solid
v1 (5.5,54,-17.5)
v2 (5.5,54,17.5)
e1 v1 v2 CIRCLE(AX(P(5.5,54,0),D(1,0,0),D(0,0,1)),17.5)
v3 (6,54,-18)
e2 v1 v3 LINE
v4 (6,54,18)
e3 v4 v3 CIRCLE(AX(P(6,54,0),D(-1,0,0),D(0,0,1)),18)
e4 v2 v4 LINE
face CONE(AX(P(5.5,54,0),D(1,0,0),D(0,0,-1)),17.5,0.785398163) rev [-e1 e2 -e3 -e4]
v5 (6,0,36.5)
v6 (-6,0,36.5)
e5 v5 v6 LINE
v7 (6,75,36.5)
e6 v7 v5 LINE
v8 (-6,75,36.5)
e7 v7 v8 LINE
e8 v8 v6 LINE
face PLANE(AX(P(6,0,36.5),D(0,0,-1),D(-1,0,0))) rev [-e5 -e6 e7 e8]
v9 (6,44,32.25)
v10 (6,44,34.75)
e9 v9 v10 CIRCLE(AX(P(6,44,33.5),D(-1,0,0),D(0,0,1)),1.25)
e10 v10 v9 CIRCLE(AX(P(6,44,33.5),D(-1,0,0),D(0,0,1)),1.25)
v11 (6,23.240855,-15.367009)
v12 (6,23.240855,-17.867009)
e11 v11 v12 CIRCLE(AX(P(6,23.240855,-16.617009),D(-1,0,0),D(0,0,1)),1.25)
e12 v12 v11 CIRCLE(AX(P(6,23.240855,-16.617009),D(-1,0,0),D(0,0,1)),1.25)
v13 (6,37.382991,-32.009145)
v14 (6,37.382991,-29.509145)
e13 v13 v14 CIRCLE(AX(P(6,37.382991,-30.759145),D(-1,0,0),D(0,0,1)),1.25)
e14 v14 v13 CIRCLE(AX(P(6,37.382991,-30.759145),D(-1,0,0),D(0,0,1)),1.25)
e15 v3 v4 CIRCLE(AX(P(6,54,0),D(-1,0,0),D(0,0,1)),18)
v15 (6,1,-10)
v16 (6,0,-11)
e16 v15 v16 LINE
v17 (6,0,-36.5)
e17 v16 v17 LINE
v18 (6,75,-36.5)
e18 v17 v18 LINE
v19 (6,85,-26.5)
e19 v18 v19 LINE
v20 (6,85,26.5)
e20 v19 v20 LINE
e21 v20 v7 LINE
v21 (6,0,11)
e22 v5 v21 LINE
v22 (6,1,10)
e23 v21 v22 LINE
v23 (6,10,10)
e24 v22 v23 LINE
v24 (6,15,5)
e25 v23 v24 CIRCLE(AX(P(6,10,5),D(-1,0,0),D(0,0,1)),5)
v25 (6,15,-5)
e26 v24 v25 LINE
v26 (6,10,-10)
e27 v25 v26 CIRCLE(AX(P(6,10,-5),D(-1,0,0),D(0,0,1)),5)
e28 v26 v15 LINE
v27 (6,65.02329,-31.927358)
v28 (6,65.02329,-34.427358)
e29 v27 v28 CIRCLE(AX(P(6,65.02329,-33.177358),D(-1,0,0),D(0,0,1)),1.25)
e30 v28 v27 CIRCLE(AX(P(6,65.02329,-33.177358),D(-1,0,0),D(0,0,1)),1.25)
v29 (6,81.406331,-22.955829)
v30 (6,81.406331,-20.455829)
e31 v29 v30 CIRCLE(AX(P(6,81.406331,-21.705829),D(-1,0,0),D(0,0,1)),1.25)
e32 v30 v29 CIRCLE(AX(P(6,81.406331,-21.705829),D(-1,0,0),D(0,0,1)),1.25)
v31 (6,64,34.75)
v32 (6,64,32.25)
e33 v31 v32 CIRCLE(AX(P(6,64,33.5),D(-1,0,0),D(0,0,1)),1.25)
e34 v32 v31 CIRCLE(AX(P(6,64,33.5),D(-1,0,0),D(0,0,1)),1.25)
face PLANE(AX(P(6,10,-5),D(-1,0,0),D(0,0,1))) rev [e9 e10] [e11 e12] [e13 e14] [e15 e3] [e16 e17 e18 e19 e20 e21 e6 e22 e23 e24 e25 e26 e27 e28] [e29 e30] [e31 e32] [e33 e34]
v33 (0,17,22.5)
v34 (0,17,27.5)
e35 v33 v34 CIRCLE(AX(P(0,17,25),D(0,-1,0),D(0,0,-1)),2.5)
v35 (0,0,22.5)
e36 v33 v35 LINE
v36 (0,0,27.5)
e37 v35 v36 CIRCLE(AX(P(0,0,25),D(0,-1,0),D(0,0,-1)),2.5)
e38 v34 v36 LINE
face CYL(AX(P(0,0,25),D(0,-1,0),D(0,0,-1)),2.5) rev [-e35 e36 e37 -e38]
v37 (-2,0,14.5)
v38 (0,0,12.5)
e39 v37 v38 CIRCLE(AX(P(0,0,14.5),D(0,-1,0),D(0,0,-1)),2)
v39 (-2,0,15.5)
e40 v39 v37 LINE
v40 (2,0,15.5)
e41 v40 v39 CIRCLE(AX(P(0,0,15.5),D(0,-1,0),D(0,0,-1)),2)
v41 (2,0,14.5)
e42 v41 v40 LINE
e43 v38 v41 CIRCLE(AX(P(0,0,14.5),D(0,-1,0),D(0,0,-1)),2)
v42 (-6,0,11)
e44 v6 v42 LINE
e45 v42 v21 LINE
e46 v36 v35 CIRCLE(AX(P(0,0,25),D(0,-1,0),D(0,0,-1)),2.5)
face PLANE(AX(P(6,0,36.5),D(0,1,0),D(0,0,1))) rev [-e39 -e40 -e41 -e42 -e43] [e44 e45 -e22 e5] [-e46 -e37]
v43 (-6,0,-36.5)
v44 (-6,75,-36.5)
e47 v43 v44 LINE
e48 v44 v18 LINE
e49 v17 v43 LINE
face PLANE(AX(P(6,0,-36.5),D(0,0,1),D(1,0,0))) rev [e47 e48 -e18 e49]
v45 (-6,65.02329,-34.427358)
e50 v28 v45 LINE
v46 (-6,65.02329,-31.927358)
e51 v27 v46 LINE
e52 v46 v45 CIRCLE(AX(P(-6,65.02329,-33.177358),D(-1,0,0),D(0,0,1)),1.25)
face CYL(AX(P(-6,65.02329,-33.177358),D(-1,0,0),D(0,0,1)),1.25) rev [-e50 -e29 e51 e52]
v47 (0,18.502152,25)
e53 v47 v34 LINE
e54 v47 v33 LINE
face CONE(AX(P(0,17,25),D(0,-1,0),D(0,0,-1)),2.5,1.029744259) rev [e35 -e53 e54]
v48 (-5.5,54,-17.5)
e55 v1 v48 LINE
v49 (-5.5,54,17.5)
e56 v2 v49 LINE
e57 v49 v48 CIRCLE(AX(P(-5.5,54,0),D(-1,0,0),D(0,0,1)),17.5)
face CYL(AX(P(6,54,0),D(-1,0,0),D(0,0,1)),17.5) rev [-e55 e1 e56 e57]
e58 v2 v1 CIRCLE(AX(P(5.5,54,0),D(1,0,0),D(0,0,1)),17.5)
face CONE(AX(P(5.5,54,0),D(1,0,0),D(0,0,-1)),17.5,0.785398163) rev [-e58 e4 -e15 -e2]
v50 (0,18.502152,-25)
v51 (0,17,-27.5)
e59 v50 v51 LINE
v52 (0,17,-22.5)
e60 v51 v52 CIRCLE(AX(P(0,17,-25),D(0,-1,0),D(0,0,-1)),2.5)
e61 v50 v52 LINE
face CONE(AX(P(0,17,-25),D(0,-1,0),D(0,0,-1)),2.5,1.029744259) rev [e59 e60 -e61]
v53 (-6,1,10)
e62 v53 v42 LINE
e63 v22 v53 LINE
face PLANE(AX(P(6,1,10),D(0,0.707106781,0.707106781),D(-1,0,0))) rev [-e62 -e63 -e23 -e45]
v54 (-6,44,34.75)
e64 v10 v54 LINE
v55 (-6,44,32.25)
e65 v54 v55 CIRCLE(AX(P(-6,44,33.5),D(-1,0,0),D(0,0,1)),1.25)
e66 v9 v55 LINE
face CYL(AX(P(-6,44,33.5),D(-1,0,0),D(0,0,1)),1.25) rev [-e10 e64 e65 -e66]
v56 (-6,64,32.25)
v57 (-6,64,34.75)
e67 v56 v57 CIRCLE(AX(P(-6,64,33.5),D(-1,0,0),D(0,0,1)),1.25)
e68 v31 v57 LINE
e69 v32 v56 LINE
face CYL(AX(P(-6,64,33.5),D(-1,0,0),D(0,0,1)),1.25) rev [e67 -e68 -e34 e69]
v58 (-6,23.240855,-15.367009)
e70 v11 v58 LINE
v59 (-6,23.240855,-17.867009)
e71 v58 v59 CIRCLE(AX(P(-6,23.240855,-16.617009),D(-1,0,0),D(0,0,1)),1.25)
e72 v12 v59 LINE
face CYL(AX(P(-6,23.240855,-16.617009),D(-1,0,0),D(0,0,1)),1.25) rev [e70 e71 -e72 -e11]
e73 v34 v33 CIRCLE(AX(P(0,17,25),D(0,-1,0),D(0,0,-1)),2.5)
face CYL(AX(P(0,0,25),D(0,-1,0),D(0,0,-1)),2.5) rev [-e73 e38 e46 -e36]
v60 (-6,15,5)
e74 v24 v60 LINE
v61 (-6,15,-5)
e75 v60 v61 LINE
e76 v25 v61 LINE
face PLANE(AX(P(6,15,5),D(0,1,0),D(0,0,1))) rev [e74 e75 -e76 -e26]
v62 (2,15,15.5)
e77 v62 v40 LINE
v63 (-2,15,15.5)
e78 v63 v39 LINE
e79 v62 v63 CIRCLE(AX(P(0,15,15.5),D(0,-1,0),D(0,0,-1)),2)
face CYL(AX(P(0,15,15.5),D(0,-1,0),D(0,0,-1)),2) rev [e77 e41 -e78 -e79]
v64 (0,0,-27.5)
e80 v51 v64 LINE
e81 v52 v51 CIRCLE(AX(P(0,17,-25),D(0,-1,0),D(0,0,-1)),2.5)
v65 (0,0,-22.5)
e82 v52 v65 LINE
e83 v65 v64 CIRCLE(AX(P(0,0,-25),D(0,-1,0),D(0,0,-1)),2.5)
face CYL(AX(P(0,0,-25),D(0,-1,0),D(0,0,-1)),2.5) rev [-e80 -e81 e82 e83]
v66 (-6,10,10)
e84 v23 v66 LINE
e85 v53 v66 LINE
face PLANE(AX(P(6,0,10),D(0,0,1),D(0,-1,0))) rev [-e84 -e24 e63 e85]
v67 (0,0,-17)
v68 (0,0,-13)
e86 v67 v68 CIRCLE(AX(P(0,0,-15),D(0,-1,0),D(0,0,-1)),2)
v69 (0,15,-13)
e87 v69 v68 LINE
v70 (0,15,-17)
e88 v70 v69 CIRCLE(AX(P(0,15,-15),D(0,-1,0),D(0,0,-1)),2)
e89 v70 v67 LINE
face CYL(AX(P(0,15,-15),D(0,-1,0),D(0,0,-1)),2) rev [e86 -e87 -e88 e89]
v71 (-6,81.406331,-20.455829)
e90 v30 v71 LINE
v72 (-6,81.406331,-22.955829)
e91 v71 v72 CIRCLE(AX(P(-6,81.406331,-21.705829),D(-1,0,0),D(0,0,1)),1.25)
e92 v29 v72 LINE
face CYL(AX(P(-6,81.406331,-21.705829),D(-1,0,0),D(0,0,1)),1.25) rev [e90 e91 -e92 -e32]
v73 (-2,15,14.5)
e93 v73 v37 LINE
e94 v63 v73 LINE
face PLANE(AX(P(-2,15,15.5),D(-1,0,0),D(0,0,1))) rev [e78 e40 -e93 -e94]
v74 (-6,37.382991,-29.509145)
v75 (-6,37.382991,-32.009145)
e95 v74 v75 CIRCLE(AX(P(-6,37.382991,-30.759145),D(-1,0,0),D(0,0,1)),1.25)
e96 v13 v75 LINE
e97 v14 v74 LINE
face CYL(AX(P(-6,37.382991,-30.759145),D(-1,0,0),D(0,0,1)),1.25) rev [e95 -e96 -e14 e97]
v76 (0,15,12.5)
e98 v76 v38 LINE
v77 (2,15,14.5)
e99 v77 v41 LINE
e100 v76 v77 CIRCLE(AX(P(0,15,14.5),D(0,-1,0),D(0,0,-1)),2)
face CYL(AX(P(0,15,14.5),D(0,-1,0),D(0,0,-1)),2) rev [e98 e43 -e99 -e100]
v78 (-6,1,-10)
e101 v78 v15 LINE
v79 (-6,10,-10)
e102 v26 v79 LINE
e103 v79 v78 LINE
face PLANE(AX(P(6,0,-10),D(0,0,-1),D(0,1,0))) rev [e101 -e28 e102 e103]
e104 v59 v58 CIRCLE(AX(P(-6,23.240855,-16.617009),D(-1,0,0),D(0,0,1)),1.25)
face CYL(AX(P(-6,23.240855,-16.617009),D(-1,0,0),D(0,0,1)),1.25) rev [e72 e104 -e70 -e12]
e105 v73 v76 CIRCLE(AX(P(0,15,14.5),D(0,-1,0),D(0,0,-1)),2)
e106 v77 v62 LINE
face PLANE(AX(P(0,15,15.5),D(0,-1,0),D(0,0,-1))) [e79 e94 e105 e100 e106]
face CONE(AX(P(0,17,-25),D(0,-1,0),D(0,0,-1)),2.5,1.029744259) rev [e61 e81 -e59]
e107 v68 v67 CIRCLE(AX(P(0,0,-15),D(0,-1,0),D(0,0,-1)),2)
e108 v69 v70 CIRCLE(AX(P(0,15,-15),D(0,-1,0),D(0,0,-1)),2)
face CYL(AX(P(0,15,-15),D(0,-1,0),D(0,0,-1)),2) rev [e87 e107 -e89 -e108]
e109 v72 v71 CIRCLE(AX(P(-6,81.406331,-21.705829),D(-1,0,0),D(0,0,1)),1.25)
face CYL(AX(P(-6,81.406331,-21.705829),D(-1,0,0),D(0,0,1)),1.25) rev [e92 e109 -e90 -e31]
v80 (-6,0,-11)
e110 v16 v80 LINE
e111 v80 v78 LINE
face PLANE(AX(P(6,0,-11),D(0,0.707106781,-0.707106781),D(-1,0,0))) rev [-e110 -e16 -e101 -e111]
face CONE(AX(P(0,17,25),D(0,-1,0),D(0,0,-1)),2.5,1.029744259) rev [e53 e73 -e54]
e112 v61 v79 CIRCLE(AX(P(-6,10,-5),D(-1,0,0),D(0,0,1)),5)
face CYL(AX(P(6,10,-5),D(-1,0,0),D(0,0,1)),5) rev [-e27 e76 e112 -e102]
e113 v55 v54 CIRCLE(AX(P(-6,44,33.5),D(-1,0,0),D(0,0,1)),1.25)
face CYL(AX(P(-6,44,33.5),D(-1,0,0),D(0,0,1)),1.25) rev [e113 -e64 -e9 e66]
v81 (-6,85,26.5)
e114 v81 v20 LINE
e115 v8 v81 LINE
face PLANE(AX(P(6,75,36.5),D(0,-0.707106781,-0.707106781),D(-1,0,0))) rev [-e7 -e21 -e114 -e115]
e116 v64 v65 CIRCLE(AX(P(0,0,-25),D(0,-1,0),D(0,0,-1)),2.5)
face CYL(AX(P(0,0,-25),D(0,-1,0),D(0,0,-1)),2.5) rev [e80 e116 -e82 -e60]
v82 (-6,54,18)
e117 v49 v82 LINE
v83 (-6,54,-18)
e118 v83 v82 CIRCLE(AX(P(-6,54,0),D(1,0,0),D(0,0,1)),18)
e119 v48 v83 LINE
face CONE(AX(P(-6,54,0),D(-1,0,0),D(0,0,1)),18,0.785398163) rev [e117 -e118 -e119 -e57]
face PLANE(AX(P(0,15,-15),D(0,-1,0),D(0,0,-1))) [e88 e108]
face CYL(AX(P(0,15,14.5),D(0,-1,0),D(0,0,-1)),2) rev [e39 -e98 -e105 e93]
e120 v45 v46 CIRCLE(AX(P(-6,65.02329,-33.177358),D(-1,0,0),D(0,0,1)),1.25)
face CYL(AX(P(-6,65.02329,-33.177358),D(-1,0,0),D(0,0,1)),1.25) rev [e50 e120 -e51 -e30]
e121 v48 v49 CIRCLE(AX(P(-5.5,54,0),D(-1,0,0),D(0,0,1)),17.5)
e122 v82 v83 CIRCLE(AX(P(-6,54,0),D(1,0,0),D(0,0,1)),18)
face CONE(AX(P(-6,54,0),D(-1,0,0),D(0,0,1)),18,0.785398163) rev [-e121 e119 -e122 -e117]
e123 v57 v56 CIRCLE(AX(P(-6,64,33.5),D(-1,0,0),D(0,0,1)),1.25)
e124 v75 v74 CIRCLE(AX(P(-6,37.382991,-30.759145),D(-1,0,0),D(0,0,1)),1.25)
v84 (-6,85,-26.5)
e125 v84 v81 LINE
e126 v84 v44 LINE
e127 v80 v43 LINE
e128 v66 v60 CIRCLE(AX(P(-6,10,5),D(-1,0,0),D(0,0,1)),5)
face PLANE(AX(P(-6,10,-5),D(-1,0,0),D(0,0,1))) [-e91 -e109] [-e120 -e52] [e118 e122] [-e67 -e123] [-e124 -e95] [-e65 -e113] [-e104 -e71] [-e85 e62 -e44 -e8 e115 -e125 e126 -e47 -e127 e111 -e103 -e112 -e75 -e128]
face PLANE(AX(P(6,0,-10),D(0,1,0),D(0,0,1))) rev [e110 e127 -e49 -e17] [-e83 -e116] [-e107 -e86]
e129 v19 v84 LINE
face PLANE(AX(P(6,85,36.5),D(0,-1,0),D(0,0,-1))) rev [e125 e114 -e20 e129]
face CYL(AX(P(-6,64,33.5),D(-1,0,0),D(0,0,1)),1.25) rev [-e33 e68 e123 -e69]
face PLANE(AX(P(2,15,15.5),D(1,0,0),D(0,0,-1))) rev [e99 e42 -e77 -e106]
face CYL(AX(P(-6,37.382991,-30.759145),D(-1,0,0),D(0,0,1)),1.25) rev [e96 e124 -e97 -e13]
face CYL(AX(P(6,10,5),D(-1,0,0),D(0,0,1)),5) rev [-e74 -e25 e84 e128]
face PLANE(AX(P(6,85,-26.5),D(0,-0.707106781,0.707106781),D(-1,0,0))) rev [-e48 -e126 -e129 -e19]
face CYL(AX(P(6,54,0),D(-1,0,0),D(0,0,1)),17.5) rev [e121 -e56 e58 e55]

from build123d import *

# Parameters (mm, degrees)
SKETCH1_R             = 17.5
BOSS_EXTRUDE1_DEPTH   = 6
CHAMFER1_SIZE         = 10
M6_TAPPED_HOLE1_D     = 5
M6_TAPPED_HOLE1_DEPTH = 17
M6_TAPPED_HOLE1_TIP   = 1.502151548
SKETCH8_R             = 2
CUT_EXTRUDE1_DEPTH    = 15
CHAMFER2_SIZE         = 1
M3_TAPPED_HOLE1_D     = 2.5
CHAMFER3_SIZE         = 0.5


with BuildPart() as part:
    # Sketch1 → Boss-Extrude1 (new, symmetric)
    with BuildSketch(Plane(origin=(0, 0, 0), x_dir=(0, 0, -1), z_dir=(1, 0, 0))):
        with BuildLine():
            Line((-36.5, 0), (-10, 0))
            Line((-10, 0), (-10, 10))
            ThreePointArc((-10, 10), (-8.535533906, 13.535533906), (-5, 15))
            Line((-5, 15), (5, 15))
            ThreePointArc((5, 15), (8.535533906, 13.535533906), (10, 10))
            Line((10, 10), (10, 0))
            Line((10, 0), (36.5, 0))
            Line((36.5, 0), (36.5, 85))
            Line((36.5, 85), (-36.5, 85))
            Line((-36.5, 85), (-36.5, 0))
        make_face()
        with Locations((0, 54)):
            Circle(SKETCH1_R, mode=Mode.SUBTRACT)
    extrude(amount=BOSS_EXTRUDE1_DEPTH, both=True)

    # Chamfer1
    chamfer1_edges = [part.edges().sort_by_distance(p)[0] for p in [
        (0, 85, 36.5),
        (0, 85, -36.5),
    ]]
    chamfer(chamfer1_edges, length=CHAMFER1_SIZE)

    # M6 Tapped Hole1
    with Locations(Plane(origin=(0, 0, 0), x_dir=(-1, 0, 0), z_dir=(0, -1, 0))):
        with Locations((0, -25), (0, 25)):
            Hole(M6_TAPPED_HOLE1_D / 2, depth=M6_TAPPED_HOLE1_DEPTH)
            with Locations((0, 0, -(M6_TAPPED_HOLE1_DEPTH + M6_TAPPED_HOLE1_TIP / 2))):  # 118° drill point
                Cone(0, M6_TAPPED_HOLE1_D / 2, M6_TAPPED_HOLE1_TIP, mode=Mode.SUBTRACT)

    # Sketch8 → Cut-Extrude1 (cut)
    with BuildSketch(Plane.XZ):
        with Locations(Location((0, -15, 0), (0, 0, 270))):
            Circle(SKETCH8_R)
        with BuildLine():
            Line((2, 15.5), (2, 14.5))
            ThreePointArc((2, 14.5), (0, 12.5), (-2, 14.5))
            Line((-2, 14.5), (-2, 15.5))
            ThreePointArc((-2, 15.5), (0, 17.5), (2, 15.5))
        make_face()
    extrude(amount=-CUT_EXTRUDE1_DEPTH, mode=Mode.SUBTRACT)

    # Chamfer2
    chamfer2_edges = [part.edges().sort_by_distance(p)[0] for p in [
        (0, 0, -10),
        (0, 0, 10),
    ]]
    chamfer(chamfer2_edges, length=CHAMFER2_SIZE)

    # M3 Tapped Hole1 (through all)
    with Locations(Plane.ZY.offset(6)):
        with Locations((33.5, 44), (33.5, 64), (-16.617009358, 23.240855018), (-30.759144982, 37.382990642), (-33.177357847, 65.023290175), (-21.70582912, 81.406331061)):
            Hole(M3_TAPPED_HOLE1_D / 2)

    # Chamfer3
    chamfer3_edges = [part.edges().sort_by_distance(p)[0] for p in [
        (-6, 54, 17.5),
        (6, 54, 17.5),
    ]]
    chamfer(chamfer3_edges, length=CHAMFER3_SIZE)


solid = part.part
